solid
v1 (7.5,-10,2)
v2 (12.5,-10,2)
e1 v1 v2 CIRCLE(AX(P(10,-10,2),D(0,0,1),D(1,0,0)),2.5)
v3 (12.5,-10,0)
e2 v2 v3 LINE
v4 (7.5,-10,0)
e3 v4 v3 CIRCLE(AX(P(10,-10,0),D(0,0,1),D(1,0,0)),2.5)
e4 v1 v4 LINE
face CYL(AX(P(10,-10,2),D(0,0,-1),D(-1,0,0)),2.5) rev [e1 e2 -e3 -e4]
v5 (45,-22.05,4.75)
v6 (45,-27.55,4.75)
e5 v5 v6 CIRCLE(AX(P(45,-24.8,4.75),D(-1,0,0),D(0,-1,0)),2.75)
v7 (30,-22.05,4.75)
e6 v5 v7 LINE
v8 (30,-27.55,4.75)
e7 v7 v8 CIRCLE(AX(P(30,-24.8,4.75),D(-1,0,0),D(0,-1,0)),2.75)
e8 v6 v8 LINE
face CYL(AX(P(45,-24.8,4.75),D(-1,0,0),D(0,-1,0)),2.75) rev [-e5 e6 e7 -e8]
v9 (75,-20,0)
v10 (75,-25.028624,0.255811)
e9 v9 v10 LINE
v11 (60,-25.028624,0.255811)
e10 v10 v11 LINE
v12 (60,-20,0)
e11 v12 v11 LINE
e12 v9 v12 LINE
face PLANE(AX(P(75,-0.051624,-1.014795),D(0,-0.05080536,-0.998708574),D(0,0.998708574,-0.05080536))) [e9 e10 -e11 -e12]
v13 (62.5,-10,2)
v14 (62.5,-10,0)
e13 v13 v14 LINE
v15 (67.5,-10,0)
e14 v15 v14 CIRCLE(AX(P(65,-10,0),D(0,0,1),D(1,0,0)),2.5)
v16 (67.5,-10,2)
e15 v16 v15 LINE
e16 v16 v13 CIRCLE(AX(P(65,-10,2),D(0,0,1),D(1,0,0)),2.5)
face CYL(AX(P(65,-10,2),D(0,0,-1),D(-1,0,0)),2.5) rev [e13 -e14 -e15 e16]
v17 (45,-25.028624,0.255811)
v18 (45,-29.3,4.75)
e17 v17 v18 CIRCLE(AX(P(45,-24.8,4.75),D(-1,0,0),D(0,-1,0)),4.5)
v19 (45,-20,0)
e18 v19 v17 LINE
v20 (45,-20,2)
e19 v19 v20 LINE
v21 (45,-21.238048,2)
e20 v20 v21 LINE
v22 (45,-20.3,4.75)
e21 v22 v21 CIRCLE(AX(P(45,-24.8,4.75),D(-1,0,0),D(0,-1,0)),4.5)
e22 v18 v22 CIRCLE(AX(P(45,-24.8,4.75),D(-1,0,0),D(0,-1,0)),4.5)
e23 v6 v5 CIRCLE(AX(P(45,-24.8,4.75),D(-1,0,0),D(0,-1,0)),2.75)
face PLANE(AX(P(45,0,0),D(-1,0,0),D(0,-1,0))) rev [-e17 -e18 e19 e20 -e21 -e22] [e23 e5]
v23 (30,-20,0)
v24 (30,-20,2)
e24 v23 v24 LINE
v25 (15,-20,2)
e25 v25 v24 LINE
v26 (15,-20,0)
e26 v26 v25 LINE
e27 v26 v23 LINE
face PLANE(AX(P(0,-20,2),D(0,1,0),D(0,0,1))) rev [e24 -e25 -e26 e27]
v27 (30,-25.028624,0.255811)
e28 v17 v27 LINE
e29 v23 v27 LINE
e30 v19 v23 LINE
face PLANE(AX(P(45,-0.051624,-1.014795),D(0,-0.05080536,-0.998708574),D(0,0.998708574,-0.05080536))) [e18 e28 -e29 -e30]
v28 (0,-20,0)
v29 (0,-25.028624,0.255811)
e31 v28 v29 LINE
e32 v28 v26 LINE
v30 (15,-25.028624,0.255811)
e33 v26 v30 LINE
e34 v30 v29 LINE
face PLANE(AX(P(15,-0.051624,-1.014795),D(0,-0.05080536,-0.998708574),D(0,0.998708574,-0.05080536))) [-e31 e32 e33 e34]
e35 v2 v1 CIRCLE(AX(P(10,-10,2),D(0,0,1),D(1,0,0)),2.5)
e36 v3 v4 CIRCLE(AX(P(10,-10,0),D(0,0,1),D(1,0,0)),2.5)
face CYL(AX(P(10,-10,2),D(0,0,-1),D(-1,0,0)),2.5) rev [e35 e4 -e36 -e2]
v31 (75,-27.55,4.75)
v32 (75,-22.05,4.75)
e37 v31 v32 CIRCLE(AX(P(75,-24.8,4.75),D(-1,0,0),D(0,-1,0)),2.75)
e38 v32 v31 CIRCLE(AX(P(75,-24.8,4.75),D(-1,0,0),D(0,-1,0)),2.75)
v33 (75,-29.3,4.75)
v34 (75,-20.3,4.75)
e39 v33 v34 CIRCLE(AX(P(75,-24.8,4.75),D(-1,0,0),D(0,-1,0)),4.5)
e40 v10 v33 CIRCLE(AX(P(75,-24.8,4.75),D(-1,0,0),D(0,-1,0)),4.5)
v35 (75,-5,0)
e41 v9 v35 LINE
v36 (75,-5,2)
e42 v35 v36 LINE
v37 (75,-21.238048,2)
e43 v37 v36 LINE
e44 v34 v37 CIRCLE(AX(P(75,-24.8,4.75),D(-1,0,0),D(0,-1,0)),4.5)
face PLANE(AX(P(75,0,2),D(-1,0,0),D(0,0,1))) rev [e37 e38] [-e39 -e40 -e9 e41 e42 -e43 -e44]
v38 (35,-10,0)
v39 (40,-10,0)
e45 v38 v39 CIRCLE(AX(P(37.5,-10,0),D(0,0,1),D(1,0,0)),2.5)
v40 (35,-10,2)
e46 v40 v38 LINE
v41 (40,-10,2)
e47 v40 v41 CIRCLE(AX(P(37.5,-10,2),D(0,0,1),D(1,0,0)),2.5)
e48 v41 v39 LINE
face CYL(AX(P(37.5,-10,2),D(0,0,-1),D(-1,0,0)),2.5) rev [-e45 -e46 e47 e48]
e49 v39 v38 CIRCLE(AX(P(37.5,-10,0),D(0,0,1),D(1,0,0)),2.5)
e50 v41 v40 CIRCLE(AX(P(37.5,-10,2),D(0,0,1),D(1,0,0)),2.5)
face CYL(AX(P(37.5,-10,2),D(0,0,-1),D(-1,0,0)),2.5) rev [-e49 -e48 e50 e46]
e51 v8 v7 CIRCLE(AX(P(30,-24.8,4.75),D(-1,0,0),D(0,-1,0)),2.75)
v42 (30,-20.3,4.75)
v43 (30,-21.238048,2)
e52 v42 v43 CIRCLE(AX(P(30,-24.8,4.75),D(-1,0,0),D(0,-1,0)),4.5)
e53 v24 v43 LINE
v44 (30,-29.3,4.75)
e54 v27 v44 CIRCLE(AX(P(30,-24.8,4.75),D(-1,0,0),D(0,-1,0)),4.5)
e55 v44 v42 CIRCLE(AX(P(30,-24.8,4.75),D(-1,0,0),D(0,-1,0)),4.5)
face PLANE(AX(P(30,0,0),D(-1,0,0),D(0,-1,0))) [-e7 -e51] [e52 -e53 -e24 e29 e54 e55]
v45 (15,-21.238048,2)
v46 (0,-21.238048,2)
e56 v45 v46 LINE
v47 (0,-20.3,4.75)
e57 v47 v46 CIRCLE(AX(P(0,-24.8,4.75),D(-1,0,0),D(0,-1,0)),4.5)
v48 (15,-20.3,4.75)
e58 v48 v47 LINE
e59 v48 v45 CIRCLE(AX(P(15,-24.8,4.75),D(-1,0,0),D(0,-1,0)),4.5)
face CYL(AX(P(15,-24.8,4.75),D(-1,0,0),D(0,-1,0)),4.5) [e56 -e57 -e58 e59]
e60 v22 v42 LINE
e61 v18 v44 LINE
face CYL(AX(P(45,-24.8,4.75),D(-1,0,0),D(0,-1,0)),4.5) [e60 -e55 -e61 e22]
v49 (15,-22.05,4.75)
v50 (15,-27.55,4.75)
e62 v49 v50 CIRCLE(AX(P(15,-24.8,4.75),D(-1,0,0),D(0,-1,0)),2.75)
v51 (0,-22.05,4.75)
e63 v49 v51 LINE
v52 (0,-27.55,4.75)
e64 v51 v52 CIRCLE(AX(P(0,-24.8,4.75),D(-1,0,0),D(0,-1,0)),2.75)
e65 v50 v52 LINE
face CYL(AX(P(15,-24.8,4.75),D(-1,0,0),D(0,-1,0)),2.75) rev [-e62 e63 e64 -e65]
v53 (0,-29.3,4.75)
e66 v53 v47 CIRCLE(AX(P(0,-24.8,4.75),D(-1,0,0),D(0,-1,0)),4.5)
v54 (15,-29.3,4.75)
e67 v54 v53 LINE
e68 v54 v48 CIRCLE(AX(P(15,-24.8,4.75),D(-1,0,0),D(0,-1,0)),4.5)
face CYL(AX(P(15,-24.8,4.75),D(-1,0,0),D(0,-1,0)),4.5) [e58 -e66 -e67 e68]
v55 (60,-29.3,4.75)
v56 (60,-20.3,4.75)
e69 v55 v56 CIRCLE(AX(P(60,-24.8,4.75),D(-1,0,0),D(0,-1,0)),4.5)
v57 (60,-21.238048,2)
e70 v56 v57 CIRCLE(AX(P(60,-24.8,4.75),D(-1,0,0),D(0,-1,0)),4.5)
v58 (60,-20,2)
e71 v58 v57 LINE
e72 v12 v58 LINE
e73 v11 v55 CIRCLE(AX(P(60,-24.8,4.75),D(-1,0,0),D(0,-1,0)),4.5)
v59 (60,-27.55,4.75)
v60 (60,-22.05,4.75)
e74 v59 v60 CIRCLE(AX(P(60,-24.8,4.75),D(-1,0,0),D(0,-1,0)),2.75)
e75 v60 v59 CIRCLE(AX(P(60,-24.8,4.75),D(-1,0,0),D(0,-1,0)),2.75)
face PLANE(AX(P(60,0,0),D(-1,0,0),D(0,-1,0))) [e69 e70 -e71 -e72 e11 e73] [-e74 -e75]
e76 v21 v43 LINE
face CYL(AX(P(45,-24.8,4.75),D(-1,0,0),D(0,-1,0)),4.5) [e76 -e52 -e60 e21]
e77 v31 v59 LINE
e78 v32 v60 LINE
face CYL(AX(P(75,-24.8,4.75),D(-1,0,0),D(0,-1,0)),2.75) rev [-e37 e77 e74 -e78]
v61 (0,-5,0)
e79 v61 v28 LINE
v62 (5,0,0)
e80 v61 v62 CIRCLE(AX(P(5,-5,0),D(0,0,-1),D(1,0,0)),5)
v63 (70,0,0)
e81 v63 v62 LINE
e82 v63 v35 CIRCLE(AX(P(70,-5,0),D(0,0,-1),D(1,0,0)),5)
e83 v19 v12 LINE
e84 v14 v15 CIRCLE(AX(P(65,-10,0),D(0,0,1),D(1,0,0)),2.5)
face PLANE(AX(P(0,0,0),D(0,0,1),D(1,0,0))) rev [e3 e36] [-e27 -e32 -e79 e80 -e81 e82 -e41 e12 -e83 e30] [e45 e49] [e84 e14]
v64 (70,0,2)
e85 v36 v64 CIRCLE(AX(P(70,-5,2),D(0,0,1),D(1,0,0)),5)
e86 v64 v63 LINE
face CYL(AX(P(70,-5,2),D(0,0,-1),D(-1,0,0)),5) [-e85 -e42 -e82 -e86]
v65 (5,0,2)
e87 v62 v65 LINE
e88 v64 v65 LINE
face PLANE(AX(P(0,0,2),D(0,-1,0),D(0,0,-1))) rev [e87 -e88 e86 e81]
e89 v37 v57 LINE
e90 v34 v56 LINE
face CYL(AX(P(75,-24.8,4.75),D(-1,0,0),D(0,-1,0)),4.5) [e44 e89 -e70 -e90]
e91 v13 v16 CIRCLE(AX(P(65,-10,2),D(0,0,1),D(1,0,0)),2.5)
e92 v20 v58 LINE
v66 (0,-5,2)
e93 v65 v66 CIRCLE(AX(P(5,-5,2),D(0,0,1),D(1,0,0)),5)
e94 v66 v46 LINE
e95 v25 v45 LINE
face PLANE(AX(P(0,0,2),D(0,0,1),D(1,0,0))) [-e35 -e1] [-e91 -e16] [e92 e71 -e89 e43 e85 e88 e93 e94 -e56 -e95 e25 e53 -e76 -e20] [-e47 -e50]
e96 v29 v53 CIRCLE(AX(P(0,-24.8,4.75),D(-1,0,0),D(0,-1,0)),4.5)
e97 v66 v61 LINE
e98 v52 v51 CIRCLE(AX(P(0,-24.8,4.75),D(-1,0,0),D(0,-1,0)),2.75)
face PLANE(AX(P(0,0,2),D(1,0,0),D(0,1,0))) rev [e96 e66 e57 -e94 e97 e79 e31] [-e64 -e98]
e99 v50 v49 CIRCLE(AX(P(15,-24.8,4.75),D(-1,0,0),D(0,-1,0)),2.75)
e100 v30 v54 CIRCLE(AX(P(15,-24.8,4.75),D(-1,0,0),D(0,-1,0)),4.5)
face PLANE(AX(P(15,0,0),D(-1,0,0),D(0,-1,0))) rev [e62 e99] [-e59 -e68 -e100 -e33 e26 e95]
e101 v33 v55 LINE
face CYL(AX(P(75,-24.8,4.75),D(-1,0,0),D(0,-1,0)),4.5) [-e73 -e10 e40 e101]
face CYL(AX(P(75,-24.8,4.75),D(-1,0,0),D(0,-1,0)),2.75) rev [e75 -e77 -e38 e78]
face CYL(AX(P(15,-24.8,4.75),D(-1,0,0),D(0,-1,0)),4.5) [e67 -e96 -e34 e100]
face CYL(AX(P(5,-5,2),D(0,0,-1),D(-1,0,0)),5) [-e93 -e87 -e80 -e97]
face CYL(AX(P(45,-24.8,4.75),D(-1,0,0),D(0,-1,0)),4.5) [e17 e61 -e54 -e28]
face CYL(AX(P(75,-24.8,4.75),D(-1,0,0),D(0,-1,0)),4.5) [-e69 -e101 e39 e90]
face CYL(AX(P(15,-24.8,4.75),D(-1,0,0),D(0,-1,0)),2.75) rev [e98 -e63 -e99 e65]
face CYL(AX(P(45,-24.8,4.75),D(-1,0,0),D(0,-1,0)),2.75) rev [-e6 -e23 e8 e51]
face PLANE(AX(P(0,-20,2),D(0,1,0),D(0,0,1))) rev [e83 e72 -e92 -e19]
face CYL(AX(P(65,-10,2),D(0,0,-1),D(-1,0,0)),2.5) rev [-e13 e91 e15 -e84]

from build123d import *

# Parameters (mm, degrees)
SKETCH1_W           = 75
SKETCH1_H           = 20
SKETCH1_R           = 2.5
BOSS_EXTRUDE1_DEPTH = 2
BOSS_EXTRUDE2_DEPTH = 15
LPATTERN1_COUNT     = 3
LPATTERN1_PITCH     = 30
FILLET1_R           = 5


with BuildPart() as part:
    # Sketch1 → Boss-Extrude1 (new body)
    with BuildSketch(Plane.XY):
        with Locations((37.5, -10)):
            Rectangle(SKETCH1_W, SKETCH1_H)
        with Locations((10, -10)):
            Circle(SKETCH1_R, mode=Mode.SUBTRACT)
        with Locations((65, -10)):
            Circle(SKETCH1_R, mode=Mode.SUBTRACT)
        with Locations((37.5, -10)):
            Circle(SKETCH1_R, mode=Mode.SUBTRACT)
    extrude(amount=BOSS_EXTRUDE1_DEPTH)

    # Sketch2 → Boss-Extrude2 (add)
    # profile 1 of 2: a face of its own
    with BuildSketch(Plane.ZY):
        with BuildLine():
            ThreePointArc((2, -28.361951712), (9.25, -24.8), (2, -21.238048288))
            Line((2, -21.238048288), (2, -24.8))
            Line((2, -24.8), (2, -28.361951712))
        make_face()
        with BuildLine():
            ThreePointArc((7.5, -24.8), (4.75, -27.55), (2, -24.8))
            ThreePointArc((2, -24.8), (4.75, -22.05), (7.5, -24.8))
        make_face(mode=Mode.SUBTRACT)
    # profile 2 of 2: a face of its own
    with BuildSketch(Plane.ZY):
        with BuildLine():
            Line((2, -21.238048288), (2, -20))
            Line((2, -20), (0, -20))
            Line((0, -20), (0.255811418, -25.028624118))
            ThreePointArc((0.255811418, -25.028624118), (0.762853744, -26.886304085), (2, -28.361951712))
            Line((2, -28.361951712), (2, -24.8))
            Line((2, -24.8), (2, -21.238048288))
        make_face()
    boss_extrude2 = extrude(amount=-BOSS_EXTRUDE2_DEPTH)

    # LPattern1: Boss-Extrude2 ×3
    with Locations(*[(i * LPATTERN1_PITCH, 0, 0) for i in range(1, LPATTERN1_COUNT)]):
        add(boss_extrude2)

    # Fillet1
    fillet1_edges = [part.edges().sort_by_distance(p)[0] for p in [
        (0, 0, 1),
        (75, 0, 1),
    ]]
    fillet(fillet1_edges, radius=FILLET1_R)


solid = part.part
